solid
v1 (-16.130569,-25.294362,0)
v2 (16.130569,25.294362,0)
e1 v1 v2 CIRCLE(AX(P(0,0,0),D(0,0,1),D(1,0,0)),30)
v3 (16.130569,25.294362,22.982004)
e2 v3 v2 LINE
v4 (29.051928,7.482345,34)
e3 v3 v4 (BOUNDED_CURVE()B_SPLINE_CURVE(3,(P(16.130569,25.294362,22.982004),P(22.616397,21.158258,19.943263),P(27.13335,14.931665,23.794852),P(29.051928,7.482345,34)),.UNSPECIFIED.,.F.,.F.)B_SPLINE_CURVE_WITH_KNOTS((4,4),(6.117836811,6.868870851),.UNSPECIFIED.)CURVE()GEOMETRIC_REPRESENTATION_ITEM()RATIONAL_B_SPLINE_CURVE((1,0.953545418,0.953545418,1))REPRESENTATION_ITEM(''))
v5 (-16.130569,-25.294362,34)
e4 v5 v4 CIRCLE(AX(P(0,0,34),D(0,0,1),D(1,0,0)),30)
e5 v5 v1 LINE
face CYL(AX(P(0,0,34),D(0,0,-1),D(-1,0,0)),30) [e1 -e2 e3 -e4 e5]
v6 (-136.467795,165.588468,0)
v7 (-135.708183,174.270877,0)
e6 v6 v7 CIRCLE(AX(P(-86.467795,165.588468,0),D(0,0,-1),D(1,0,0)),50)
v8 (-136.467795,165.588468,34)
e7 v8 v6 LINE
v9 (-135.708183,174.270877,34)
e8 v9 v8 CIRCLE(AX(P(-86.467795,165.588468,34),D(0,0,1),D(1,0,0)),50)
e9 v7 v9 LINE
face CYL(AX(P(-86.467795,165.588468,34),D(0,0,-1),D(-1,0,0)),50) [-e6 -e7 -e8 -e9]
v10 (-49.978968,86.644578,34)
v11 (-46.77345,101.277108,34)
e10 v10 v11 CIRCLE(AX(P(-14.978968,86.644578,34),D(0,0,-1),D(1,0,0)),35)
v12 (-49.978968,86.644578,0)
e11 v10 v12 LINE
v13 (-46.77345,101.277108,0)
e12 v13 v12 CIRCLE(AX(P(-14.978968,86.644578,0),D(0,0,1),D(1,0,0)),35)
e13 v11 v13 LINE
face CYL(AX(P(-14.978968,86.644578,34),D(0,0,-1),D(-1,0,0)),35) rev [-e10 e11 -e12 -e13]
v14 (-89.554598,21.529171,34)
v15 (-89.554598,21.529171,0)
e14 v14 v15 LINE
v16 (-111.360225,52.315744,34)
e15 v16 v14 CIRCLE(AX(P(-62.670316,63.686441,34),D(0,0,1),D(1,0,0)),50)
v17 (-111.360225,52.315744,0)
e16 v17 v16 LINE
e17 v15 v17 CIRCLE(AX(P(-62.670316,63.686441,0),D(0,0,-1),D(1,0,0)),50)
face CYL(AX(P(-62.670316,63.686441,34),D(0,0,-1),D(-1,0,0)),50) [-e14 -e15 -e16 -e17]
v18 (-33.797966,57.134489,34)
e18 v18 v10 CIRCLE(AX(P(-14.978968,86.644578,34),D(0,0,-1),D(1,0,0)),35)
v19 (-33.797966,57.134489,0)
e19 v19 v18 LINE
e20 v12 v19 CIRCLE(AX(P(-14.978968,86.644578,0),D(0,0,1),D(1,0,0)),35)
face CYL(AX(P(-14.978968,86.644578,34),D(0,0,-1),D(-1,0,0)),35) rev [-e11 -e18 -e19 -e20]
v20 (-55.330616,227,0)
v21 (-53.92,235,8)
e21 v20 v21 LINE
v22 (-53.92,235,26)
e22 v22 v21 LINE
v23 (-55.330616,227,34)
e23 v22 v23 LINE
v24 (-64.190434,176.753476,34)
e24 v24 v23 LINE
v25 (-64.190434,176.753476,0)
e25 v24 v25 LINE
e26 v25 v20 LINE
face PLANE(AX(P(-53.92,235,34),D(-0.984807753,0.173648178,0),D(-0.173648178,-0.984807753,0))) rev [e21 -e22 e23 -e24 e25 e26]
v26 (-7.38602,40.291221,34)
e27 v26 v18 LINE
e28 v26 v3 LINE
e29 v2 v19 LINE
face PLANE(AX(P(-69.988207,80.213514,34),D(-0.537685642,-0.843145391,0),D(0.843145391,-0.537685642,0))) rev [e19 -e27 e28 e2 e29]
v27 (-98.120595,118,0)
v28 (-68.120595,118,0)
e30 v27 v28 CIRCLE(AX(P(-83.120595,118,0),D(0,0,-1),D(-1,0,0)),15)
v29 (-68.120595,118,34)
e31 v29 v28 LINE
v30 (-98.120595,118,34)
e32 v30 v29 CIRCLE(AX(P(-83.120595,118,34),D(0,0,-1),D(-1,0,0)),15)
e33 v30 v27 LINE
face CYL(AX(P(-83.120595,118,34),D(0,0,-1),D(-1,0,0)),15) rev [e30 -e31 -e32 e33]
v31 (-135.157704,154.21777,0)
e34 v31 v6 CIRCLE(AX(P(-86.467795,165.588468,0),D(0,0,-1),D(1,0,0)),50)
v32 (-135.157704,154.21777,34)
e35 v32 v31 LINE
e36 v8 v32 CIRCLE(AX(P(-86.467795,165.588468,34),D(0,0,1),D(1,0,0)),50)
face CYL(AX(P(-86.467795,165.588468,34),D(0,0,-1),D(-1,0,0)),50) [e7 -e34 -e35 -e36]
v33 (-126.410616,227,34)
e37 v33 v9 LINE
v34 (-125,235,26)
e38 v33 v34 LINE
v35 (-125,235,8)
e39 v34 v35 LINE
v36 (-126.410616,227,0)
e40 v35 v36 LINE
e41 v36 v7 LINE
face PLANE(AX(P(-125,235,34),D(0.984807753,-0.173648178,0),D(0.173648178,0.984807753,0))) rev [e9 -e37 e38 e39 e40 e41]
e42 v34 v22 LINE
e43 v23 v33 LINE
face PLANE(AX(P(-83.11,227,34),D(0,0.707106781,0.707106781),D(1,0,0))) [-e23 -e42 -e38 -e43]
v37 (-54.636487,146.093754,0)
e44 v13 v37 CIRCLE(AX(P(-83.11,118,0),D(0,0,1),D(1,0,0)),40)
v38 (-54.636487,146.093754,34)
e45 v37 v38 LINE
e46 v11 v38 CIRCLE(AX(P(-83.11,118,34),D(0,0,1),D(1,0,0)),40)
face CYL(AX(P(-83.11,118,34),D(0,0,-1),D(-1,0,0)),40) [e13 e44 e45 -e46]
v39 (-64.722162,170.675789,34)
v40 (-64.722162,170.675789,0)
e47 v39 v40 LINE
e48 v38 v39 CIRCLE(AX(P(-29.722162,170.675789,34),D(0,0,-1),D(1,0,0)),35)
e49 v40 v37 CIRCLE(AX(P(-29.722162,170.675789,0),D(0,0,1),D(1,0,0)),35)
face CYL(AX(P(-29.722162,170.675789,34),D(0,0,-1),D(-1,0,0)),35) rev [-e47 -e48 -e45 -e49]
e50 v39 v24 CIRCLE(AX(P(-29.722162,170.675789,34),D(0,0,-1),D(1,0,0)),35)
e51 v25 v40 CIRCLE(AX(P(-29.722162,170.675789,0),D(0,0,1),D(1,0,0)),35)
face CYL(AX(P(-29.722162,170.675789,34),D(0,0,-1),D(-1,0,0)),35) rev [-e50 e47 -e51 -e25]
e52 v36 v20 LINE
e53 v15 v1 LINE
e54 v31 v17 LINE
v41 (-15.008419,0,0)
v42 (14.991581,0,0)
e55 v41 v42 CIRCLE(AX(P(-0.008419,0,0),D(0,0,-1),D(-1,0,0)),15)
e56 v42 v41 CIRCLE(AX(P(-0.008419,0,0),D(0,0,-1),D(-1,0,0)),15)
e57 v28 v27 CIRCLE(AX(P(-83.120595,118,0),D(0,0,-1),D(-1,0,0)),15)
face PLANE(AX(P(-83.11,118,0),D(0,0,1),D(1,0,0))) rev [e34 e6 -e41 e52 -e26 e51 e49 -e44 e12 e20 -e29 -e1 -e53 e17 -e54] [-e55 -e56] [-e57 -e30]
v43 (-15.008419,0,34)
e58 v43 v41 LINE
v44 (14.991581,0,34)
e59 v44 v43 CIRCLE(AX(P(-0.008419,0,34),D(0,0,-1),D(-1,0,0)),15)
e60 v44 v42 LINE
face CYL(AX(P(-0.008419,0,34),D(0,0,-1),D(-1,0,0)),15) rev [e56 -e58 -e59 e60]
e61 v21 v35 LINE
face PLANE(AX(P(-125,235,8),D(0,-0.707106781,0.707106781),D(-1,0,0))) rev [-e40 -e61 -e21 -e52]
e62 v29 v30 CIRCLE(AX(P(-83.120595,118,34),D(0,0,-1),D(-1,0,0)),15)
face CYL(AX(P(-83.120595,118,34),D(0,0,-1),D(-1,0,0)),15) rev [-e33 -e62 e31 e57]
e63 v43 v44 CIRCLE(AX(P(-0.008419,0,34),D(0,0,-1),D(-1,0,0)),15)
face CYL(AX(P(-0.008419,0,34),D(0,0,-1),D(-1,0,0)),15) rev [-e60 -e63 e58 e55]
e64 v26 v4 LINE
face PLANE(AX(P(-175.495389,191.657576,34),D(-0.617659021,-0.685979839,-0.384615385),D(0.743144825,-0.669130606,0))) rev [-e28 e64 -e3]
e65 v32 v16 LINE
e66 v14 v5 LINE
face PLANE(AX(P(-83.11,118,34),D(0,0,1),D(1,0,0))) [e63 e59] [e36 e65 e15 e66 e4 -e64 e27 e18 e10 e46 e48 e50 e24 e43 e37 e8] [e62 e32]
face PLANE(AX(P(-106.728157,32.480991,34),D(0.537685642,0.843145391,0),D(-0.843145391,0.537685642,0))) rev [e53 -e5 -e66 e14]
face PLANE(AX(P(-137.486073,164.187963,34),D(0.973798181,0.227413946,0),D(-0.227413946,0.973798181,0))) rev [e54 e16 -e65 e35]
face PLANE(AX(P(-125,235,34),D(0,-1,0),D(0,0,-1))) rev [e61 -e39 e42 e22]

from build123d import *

# Parameters (mm, degrees)
EXTRUDE_1_DEPTH                      = 34
CHAMFER_1_SIZE                       = 8
SKETCH_2_R                           = 15
CUT_EXTRUDE_1_DEPTH                  = 275.378242911
FILLET_2_R                           = 35
FILLET_4_R                           = 50
CUT_EXTRUDE_2_REACH                  = 275.869
CUT_EXTRUDE_2_DIRECTION_2_REACH      = 275.869
CUT_EXTRUDE_2_DIRECTION_2_END_RADIUS = 30


with BuildPart() as part:
    # 草图1 → 凸台-拉伸1 (new body)
    with BuildSketch(Plane.XY):
        with BuildLine():
            Line((-125, 235), (-53.92, 235))
            Line((-53.92, 235), (-68.018431876, 155.043819614))
            ThreePointArc((-68.018431876, 155.043819614), (-43.495979684, 123.54341), (-58.429747026, 86.521672326))
            ThreePointArc((-58.429747026, 86.521672326), (-63.94761811, 82.888703808), (-69.988207372, 80.21351355))
            Line((-69.988207372, 80.21351355), (16.130569268, 25.294361725))
            ThreePointArc((16.130569268, 25.294361725), (25.294361725, -16.130569268), (-16.130569268, -25.294361725))
            Line((-16.130569268, -25.294361725), (-106.728157023, 32.480990771))
            Line((-106.728157023, 32.480990771), (-137.486072687, 164.187962972))
            Line((-137.486072687, 164.187962972), (-125, 235))
        make_face()
    extrude(amount=EXTRUDE_1_DEPTH)

    # 倒角1
    chamfer_1_edges = [part.edges().sort_by_distance(p)[0] for p in [
        (-89.46, 235, 34),
        (-89.46, 235, 0),
    ]]
    chamfer(chamfer_1_edges, length=CHAMFER_1_SIZE)

    # 草图2 → 切除-拉伸1 (cut, through all)
    with BuildSketch(Plane(origin=(0, 0, 0), x_dir=(-1, 0, 0), z_dir=(0, 0, -1))):
        with Locations((0.008418778, 0)):
            Circle(SKETCH_2_R)
        with Locations((83.120594515, 118)):
            Circle(SKETCH_2_R)
    extrude(amount=-CUT_EXTRUDE_1_DEPTH, mode=Mode.SUBTRACT)

    # 圆角2
    fillet_2_edges = [part.edges().sort_by_distance(p)[0] for p in [
        (-69.988207372, 80.21351355, 17),
        (-68.018431876, 155.043819614, 17),
    ]]
    fillet(fillet_2_edges, radius=FILLET_2_R)

    # 圆角4
    fillet_4_edges = [part.edges().sort_by_distance(p)[0] for p in [
        (-106.728157023, 32.480990771, 17),
        (-137.486072687, 164.187962972, 17),
    ]]
    fillet(fillet_4_edges, radius=FILLET_4_R)

    # 切除-拉伸2: up to this plane
    cut_extrude_2_end = Plane(origin=(-69.988207372, 80.21351355, 34), z_dir=(-0.5376856422770575, -0.8431453908366625, 0))
    # 草图4 → 切除-拉伸2 (cut, up to the surface)
    with BuildSketch(Plane(origin=(0, 0, 0), x_dir=(0, 0, -1), z_dir=(0.7431448254773932, -0.6691306063588595, 0)), mode=Mode.PRIVATE) as cut_extrude_2_sk1:
        Polygon((-34, 25), (-22, 30), (-34, 30), align=None)
    cut_extrude_2_tool1 = split(extrude(cut_extrude_2_sk1.sketch, amount=-CUT_EXTRUDE_2_REACH, mode=Mode.PRIVATE), bisect_by=cut_extrude_2_end, keep=Keep.BOTH, mode=Mode.PRIVATE)
    add(cut_extrude_2_tool1.solids().sort_by_distance((18.958701, 21.05577, 30))[0], mode=Mode.SUBTRACT)

    # 切除-拉伸2 direction 2: up to this cylinder (the profile starts inside it)
    cut_extrude_2_direction_2_end = Plane(origin=(0, 0, 30), z_dir=(0, 0, -1)) * Cylinder(CUT_EXTRUDE_2_DIRECTION_2_END_RADIUS, 612.738, mode=Mode.PRIVATE)
    # 草图4 → 切除-拉伸2 direction 2 (cut, up to the surface)
    with BuildSketch(Plane(origin=(0, 0, 0), x_dir=(0, 0, -1), z_dir=(0.7431448254773932, -0.6691306063588595, 0)), mode=Mode.PRIVATE) as cut_extrude_2_direction_2_sk1:
        Polygon((-34, 25), (-22, 30), (-34, 30), align=None)
    cut_extrude_2_direction_2_tool1 = extrude(cut_extrude_2_direction_2_sk1.sketch, amount=CUT_EXTRUDE_2_DIRECTION_2_REACH, mode=Mode.PRIVATE) & cut_extrude_2_direction_2_end
    add(cut_extrude_2_direction_2_tool1.solids().sort_by_distance((18.958701, 21.05577, 30))[0], mode=Mode.SUBTRACT)


solid = part.part
